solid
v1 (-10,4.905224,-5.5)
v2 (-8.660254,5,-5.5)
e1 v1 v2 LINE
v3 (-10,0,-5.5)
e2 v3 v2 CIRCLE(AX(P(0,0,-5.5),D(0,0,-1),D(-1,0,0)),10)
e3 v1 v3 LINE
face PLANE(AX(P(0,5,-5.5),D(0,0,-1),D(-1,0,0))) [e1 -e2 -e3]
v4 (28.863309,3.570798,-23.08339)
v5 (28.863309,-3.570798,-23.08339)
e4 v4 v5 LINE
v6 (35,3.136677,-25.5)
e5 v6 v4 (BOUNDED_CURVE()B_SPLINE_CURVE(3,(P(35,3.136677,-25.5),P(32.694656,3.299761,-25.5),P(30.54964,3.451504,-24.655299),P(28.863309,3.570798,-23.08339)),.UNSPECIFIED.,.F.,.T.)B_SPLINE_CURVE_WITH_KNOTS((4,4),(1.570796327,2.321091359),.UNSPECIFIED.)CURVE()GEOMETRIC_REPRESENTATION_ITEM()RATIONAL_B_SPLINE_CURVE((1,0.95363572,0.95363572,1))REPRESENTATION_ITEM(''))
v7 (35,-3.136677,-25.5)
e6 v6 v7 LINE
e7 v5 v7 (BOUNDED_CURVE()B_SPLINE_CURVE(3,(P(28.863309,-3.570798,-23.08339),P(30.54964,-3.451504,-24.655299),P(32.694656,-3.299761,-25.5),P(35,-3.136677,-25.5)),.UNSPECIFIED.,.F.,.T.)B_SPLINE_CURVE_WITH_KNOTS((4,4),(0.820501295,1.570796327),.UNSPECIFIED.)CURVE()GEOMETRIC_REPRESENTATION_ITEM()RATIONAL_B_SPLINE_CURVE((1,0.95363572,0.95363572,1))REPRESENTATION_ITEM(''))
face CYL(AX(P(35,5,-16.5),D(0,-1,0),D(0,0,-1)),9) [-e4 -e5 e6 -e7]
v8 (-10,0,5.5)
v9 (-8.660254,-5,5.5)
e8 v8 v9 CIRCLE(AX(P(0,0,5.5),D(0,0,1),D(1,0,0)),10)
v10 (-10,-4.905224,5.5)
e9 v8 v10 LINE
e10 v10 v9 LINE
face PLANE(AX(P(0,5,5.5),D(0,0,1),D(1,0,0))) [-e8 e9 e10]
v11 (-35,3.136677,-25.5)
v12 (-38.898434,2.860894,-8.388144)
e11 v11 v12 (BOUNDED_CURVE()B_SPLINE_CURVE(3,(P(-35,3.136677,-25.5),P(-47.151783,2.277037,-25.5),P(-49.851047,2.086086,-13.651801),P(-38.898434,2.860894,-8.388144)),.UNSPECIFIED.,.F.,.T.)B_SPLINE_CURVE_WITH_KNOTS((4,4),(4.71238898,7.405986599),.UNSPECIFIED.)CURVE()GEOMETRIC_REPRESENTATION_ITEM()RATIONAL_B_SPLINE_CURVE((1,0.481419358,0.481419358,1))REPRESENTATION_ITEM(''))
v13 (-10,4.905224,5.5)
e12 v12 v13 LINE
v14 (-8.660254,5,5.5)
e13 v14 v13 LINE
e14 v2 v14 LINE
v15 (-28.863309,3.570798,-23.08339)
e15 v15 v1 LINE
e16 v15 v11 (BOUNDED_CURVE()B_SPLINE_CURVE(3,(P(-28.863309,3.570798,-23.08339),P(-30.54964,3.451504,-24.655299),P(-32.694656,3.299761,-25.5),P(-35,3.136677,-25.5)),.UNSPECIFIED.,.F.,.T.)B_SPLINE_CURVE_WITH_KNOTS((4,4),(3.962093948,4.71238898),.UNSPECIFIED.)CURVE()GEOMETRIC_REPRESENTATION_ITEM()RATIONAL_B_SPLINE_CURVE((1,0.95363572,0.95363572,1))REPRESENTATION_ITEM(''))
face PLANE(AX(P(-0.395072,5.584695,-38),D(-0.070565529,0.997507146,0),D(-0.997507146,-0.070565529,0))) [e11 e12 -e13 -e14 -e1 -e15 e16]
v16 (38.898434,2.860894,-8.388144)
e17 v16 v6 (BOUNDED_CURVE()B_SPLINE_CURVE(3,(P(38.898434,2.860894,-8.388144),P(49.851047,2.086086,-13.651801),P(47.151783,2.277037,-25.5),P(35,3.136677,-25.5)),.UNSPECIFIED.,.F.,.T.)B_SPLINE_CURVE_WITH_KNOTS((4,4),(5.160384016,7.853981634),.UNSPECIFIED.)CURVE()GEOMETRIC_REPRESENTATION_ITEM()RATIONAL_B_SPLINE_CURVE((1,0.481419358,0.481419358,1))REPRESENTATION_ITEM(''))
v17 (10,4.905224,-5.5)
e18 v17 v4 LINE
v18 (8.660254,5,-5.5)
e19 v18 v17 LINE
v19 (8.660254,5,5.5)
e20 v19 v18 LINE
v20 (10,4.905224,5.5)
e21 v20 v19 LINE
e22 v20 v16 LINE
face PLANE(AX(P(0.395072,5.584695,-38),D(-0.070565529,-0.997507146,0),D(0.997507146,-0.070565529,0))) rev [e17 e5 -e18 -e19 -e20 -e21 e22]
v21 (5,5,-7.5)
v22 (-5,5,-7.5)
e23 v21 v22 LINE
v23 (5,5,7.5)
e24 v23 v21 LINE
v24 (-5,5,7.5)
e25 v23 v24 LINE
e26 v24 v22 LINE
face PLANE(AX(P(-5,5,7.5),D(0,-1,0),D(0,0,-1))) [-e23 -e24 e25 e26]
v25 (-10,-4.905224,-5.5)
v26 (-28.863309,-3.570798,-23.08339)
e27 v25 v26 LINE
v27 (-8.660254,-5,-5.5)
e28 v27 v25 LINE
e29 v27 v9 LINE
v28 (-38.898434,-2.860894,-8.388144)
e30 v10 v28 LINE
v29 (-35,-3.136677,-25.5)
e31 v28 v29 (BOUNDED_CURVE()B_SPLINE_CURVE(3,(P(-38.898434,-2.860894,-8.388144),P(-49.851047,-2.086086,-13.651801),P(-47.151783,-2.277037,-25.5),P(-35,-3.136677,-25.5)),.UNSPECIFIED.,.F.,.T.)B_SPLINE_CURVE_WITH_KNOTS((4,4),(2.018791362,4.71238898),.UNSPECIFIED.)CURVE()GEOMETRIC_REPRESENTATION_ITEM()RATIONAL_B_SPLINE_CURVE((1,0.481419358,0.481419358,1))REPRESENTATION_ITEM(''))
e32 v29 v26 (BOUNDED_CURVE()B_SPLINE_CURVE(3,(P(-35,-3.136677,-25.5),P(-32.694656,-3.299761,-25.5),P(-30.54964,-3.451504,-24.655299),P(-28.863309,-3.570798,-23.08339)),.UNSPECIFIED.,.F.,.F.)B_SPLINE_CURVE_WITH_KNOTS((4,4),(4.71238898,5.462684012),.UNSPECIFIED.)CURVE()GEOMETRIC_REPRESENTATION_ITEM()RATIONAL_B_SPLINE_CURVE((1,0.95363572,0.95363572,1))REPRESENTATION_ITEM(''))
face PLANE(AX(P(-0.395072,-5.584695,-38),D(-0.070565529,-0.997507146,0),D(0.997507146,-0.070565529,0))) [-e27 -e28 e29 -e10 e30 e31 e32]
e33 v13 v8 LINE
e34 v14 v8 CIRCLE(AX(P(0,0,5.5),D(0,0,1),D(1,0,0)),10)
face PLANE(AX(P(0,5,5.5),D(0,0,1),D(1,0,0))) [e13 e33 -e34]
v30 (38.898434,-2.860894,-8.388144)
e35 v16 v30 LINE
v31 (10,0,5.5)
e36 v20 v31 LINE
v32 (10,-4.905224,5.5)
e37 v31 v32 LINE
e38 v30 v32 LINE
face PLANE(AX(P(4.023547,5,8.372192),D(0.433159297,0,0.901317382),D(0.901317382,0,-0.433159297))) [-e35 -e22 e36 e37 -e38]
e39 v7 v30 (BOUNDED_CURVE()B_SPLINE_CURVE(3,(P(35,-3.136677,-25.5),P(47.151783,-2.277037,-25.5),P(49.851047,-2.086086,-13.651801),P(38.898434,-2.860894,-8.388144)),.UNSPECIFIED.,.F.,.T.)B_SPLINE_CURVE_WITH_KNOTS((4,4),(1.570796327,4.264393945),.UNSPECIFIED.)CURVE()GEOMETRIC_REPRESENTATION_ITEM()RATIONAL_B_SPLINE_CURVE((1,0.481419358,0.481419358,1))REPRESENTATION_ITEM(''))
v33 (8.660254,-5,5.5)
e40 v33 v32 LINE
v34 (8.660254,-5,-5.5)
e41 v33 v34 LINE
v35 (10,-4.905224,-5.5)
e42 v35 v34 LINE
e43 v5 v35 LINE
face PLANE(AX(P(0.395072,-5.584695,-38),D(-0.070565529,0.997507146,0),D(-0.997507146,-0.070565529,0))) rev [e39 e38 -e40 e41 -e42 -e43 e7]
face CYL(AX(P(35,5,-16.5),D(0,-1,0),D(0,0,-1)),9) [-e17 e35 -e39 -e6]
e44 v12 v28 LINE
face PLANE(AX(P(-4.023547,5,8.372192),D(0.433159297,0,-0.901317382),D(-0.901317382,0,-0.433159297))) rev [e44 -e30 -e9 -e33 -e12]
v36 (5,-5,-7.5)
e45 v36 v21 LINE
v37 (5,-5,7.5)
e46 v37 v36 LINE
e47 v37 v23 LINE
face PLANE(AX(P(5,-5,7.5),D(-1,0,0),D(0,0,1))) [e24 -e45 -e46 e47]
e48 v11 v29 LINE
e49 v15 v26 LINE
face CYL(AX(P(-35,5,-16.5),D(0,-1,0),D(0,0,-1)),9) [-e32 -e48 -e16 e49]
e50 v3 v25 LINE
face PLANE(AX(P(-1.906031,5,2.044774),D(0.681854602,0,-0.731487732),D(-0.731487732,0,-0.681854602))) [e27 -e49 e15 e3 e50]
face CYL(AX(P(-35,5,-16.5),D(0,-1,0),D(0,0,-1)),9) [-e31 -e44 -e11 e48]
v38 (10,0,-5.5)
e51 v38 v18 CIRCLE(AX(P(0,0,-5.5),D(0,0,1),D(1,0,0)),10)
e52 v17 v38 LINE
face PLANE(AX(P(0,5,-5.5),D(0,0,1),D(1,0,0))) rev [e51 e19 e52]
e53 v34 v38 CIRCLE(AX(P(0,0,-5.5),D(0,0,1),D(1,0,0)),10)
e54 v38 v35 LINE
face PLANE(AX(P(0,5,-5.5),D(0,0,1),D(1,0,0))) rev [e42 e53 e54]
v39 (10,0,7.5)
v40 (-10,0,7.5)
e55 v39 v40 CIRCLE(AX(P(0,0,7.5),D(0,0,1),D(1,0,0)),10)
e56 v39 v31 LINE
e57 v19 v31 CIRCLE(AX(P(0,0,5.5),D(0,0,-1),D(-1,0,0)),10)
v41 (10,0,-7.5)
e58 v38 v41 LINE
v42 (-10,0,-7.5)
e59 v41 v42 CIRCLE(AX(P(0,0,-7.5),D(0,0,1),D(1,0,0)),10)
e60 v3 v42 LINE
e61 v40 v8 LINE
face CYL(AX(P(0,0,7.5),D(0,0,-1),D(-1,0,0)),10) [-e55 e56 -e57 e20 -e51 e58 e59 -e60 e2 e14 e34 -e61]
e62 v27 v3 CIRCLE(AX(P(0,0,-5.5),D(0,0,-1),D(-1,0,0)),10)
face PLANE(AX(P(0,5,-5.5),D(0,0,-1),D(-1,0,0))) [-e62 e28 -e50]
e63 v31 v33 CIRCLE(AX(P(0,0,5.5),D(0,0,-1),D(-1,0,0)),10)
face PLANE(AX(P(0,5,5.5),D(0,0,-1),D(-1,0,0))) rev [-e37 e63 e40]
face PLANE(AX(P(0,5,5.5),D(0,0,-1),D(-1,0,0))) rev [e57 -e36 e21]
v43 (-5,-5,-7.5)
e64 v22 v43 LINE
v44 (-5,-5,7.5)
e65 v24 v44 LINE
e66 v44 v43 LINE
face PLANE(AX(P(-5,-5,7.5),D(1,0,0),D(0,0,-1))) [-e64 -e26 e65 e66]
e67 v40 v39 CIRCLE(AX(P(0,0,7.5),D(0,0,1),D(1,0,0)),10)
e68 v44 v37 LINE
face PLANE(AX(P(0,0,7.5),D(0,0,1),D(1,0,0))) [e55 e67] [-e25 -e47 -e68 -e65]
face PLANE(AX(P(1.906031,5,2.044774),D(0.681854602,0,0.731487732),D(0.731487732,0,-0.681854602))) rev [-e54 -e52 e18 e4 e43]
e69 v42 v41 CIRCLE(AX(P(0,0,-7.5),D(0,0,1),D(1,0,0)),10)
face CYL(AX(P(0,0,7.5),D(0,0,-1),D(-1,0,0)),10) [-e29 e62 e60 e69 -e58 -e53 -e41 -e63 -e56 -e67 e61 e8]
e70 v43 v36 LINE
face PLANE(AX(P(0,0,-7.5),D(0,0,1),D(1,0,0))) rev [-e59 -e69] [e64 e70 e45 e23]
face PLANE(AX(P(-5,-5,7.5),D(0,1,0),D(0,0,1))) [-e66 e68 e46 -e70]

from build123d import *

# Parameters (mm, degrees)
SKETCH1_R           = 10
SKETCH1_W           = 10
SKETCH1_H           = 10
BOSS_EXTRUDE1_DEPTH = 7.5
SKETCH2_R           = 9
BOSS_EXTRUDE2_DEPTH = 5
CUT_EXTRUDE1_DEPTH  = 38


with BuildPart() as part:
    # Sketch1 → Boss-Extrude1 (new, symmetric)
    with BuildSketch(Plane.XY):
        Circle(SKETCH1_R)
        Rectangle(SKETCH1_W, SKETCH1_H, mode=Mode.SUBTRACT)
    extrude(amount=BOSS_EXTRUDE1_DEPTH, both=True)

    # Sketch2 → Boss-Extrude2 (add, symmetric)
    with BuildSketch(Plane(origin=(0, 0, 0), x_dir=(1, 0, 0), z_dir=(0, 1, 0))):
        with Locations((-35, 16.5)):
            Circle(SKETCH2_R)
        with BuildLine():
            Line((-10, 5.5), (-28.863308582, 23.083389586))
            ThreePointArc((-28.863308582, 23.083389586), (-26.746812047, 20.089552705), (-26, 16.5))
            ThreePointArc((-26, 16.5), (-30.208648574, 8.881407511), (-38.898433669, 8.388143558))
            Line((-38.898433669, 8.388143558), (-10, -5.5))
            Line((-10, -5.5), (-8, -5.5))
            Line((-8, -5.5), (-8, 5.5))
            Line((-8, 5.5), (-10, 5.5))
        make_face()
    boss_extrude2 = extrude(amount=BOSS_EXTRUDE2_DEPTH, both=True)

    # Sketch3 → Cut-Extrude1 (cut, symmetric)
    with BuildSketch(Plane.XY):
        Polygon((-51.292921798, 13.040521839), (-8.660254038, 5), (-44, 2.5), align=None)
        Polygon((-44, -2.5), (-51.292921798, -11.445050359), (-8.660254038, -5), align=None)
    cut_extrude1 = extrude(amount=CUT_EXTRUDE1_DEPTH, both=True, mode=Mode.SUBTRACT)

    # Mirror1: Boss-Extrude2, Cut-Extrude1 across plane
    add(boss_extrude2.mirror(Plane(origin=(0, 0, 0), x_dir=(0, 0, 1), z_dir=(1, 0, 0))))
    add(cut_extrude1.mirror(Plane(origin=(0, 0, 0), x_dir=(0, 0, 1), z_dir=(1, 0, 0))), mode=Mode.SUBTRACT)


solid = part.part
